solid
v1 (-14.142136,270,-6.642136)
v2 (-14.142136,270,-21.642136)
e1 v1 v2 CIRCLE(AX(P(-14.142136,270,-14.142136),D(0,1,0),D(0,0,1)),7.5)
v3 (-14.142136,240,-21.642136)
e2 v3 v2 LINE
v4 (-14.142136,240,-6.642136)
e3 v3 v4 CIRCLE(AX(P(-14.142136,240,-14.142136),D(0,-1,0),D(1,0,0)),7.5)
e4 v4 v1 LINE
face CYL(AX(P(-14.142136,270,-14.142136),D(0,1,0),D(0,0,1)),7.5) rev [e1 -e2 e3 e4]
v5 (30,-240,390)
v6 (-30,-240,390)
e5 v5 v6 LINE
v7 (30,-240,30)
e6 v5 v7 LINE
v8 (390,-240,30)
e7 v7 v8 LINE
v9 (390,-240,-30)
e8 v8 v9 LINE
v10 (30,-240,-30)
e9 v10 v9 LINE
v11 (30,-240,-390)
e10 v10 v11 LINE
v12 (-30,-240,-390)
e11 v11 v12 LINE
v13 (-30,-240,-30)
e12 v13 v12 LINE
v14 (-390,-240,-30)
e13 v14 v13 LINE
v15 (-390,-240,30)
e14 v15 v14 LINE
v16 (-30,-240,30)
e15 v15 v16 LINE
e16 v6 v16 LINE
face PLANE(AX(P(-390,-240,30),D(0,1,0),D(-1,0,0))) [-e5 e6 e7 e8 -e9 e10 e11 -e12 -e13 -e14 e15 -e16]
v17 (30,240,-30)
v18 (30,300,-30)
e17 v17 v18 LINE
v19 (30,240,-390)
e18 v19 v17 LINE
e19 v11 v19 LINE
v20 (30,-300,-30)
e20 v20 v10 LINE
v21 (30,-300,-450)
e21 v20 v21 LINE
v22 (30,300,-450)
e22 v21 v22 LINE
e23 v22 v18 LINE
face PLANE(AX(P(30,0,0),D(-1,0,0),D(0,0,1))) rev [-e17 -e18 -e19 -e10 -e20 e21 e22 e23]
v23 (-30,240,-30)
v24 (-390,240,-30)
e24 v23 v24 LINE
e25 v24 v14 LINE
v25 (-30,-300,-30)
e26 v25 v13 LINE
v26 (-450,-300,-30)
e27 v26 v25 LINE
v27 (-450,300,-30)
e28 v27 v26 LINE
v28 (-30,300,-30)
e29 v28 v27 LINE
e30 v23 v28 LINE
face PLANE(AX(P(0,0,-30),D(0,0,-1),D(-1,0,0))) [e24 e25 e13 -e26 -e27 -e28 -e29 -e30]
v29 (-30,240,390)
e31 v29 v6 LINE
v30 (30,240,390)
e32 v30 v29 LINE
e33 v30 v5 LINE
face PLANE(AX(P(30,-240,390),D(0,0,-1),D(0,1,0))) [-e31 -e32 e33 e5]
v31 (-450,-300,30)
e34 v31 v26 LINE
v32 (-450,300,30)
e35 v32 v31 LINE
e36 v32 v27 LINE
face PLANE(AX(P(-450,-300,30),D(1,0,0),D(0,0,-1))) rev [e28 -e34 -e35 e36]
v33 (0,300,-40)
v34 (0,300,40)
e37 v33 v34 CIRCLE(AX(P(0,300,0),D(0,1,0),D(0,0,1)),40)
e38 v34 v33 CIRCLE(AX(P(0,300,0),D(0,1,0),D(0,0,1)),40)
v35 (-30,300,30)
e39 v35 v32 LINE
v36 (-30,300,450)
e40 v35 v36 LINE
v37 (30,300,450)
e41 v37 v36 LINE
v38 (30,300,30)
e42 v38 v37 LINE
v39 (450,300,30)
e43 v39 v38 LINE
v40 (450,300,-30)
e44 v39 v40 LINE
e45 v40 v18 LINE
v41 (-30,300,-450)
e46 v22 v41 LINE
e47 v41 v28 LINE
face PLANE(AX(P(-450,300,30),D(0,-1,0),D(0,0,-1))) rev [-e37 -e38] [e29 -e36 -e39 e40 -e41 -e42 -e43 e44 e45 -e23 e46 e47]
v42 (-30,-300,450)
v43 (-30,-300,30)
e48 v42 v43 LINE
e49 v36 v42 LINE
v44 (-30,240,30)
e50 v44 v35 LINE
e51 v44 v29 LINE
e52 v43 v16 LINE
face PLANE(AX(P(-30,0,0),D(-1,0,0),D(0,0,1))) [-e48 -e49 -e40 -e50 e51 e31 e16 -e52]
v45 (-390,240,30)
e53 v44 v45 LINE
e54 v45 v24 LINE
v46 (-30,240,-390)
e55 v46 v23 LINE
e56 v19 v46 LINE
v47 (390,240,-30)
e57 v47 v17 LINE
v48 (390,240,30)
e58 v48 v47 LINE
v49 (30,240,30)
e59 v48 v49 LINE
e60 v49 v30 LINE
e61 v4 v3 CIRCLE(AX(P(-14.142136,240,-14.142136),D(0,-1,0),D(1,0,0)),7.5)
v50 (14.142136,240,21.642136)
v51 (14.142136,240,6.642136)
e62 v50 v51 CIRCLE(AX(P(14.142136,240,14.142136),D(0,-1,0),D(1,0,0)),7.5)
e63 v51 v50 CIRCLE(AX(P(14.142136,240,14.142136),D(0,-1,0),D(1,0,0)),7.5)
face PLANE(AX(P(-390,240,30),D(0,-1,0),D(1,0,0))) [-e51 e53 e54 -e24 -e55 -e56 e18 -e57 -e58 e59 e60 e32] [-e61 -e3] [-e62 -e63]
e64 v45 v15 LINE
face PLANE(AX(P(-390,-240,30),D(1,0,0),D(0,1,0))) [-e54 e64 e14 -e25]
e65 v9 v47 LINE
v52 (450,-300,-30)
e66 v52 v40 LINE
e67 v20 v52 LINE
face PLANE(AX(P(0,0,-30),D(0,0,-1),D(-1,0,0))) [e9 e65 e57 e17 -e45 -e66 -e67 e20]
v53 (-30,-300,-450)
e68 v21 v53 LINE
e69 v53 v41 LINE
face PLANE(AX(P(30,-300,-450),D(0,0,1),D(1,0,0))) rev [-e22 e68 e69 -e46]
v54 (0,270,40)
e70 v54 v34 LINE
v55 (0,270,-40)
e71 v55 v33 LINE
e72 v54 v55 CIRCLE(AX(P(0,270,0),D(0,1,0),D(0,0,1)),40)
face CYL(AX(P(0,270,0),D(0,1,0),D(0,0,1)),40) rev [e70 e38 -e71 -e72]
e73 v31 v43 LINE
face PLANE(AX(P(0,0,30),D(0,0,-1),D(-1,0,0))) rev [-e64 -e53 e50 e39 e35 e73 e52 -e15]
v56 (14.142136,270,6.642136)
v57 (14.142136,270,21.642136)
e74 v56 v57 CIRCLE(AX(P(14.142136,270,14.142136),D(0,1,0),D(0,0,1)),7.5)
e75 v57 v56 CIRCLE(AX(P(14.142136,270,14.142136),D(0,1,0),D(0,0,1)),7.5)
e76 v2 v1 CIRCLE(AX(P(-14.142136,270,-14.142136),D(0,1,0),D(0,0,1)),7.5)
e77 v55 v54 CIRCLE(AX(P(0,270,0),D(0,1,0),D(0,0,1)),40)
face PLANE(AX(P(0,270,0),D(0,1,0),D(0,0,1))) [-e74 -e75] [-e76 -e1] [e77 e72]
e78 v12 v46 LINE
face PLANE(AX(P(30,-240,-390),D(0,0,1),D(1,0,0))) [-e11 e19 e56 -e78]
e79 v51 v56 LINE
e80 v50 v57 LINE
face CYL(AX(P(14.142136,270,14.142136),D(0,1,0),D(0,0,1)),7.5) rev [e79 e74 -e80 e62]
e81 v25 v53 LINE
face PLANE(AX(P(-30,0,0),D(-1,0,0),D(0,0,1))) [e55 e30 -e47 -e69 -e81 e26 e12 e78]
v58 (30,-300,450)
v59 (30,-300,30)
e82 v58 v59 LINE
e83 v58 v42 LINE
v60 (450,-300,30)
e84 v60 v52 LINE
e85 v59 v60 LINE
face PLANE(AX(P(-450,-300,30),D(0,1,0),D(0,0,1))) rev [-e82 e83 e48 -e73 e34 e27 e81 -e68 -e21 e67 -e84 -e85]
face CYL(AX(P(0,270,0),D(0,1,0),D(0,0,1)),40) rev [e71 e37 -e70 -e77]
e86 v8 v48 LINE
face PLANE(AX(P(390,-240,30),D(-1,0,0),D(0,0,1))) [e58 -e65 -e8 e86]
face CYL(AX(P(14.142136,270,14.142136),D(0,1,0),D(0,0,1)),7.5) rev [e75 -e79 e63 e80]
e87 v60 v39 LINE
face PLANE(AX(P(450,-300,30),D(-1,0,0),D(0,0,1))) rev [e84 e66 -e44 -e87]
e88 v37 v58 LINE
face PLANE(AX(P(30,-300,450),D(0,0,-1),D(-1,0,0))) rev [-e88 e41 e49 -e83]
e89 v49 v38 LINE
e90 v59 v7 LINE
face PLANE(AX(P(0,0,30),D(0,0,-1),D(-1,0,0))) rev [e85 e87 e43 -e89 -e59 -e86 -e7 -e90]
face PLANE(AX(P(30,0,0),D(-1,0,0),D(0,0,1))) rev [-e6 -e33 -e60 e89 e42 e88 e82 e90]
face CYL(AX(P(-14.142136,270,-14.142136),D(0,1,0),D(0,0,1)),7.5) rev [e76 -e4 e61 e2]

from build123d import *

# Parameters (mm, degrees)
SKETCH1_W                        = 900
SKETCH1_H                        = 600
SKETCH1_W_2                      = 780
SKETCH1_H_2                      = 480
BOSS_EXTRUDE1_DEPTH              = 30
SKETCH2_W                        = 900
SKETCH2_H                        = 600
SKETCH2_W_2                      = 780
SKETCH2_H_2                      = 480
BOSS_EXTRUDE2_DEPTH              = 30
SKETCH3_R                        = 40
CUT_EXTRUDE1_DEPTH               = 30
BLIND_DOWEL_HOLE_0_SIZE_MM_D     = 15
BLIND_DOWEL_HOLE_0_SIZE_MM_DEPTH = 100
BLIND_DOWEL_HOLE_0_SIZE_MM_TIP   = 4.506454643


with BuildPart() as part:
    # Sketch1 → Boss-Extrude1 (new, symmetric)
    with BuildSketch(Plane.XY):
        Rectangle(SKETCH1_W, SKETCH1_H)
        Rectangle(SKETCH1_W_2, SKETCH1_H_2, mode=Mode.SUBTRACT)
    extrude(amount=BOSS_EXTRUDE1_DEPTH, both=True)

    # Sketch2 → Boss-Extrude2 (add, symmetric)
    with BuildSketch(Plane(origin=(0, 0, 0), x_dir=(0, 0, -1), z_dir=(1, 0, 0))):
        Rectangle(SKETCH2_W, SKETCH2_H)
        Rectangle(SKETCH2_W_2, SKETCH2_H_2, mode=Mode.SUBTRACT)
    extrude(amount=BOSS_EXTRUDE2_DEPTH, both=True)

    # Sketch3 → Cut-Extrude1 (cut)
    with BuildSketch(Plane(origin=(0, 300, 0), x_dir=(1, 0, 0), z_dir=(0, 1, 0))):
        with Locations(Location((0, 0, 0), (0, 0, 270))):
            Circle(SKETCH3_R)
    extrude(amount=-CUT_EXTRUDE1_DEPTH, mode=Mode.SUBTRACT)

    # Blind dowel hole 0 (size mm)
    with Locations(Plane(origin=(0, 270, 0), x_dir=(1, 0, 0), z_dir=(0, 1, 0))):
        with Locations((-14.142135624, 14.142135624), (14.142135624, -14.142135624)):
            Hole(BLIND_DOWEL_HOLE_0_SIZE_MM_D / 2, depth=BLIND_DOWEL_HOLE_0_SIZE_MM_DEPTH)
            with Locations((0, 0, -(BLIND_DOWEL_HOLE_0_SIZE_MM_DEPTH + BLIND_DOWEL_HOLE_0_SIZE_MM_TIP / 2))):  # 118° drill point
                Cone(0, BLIND_DOWEL_HOLE_0_SIZE_MM_D / 2, BLIND_DOWEL_HOLE_0_SIZE_MM_TIP, mode=Mode.SUBTRACT)


solid = part.part
